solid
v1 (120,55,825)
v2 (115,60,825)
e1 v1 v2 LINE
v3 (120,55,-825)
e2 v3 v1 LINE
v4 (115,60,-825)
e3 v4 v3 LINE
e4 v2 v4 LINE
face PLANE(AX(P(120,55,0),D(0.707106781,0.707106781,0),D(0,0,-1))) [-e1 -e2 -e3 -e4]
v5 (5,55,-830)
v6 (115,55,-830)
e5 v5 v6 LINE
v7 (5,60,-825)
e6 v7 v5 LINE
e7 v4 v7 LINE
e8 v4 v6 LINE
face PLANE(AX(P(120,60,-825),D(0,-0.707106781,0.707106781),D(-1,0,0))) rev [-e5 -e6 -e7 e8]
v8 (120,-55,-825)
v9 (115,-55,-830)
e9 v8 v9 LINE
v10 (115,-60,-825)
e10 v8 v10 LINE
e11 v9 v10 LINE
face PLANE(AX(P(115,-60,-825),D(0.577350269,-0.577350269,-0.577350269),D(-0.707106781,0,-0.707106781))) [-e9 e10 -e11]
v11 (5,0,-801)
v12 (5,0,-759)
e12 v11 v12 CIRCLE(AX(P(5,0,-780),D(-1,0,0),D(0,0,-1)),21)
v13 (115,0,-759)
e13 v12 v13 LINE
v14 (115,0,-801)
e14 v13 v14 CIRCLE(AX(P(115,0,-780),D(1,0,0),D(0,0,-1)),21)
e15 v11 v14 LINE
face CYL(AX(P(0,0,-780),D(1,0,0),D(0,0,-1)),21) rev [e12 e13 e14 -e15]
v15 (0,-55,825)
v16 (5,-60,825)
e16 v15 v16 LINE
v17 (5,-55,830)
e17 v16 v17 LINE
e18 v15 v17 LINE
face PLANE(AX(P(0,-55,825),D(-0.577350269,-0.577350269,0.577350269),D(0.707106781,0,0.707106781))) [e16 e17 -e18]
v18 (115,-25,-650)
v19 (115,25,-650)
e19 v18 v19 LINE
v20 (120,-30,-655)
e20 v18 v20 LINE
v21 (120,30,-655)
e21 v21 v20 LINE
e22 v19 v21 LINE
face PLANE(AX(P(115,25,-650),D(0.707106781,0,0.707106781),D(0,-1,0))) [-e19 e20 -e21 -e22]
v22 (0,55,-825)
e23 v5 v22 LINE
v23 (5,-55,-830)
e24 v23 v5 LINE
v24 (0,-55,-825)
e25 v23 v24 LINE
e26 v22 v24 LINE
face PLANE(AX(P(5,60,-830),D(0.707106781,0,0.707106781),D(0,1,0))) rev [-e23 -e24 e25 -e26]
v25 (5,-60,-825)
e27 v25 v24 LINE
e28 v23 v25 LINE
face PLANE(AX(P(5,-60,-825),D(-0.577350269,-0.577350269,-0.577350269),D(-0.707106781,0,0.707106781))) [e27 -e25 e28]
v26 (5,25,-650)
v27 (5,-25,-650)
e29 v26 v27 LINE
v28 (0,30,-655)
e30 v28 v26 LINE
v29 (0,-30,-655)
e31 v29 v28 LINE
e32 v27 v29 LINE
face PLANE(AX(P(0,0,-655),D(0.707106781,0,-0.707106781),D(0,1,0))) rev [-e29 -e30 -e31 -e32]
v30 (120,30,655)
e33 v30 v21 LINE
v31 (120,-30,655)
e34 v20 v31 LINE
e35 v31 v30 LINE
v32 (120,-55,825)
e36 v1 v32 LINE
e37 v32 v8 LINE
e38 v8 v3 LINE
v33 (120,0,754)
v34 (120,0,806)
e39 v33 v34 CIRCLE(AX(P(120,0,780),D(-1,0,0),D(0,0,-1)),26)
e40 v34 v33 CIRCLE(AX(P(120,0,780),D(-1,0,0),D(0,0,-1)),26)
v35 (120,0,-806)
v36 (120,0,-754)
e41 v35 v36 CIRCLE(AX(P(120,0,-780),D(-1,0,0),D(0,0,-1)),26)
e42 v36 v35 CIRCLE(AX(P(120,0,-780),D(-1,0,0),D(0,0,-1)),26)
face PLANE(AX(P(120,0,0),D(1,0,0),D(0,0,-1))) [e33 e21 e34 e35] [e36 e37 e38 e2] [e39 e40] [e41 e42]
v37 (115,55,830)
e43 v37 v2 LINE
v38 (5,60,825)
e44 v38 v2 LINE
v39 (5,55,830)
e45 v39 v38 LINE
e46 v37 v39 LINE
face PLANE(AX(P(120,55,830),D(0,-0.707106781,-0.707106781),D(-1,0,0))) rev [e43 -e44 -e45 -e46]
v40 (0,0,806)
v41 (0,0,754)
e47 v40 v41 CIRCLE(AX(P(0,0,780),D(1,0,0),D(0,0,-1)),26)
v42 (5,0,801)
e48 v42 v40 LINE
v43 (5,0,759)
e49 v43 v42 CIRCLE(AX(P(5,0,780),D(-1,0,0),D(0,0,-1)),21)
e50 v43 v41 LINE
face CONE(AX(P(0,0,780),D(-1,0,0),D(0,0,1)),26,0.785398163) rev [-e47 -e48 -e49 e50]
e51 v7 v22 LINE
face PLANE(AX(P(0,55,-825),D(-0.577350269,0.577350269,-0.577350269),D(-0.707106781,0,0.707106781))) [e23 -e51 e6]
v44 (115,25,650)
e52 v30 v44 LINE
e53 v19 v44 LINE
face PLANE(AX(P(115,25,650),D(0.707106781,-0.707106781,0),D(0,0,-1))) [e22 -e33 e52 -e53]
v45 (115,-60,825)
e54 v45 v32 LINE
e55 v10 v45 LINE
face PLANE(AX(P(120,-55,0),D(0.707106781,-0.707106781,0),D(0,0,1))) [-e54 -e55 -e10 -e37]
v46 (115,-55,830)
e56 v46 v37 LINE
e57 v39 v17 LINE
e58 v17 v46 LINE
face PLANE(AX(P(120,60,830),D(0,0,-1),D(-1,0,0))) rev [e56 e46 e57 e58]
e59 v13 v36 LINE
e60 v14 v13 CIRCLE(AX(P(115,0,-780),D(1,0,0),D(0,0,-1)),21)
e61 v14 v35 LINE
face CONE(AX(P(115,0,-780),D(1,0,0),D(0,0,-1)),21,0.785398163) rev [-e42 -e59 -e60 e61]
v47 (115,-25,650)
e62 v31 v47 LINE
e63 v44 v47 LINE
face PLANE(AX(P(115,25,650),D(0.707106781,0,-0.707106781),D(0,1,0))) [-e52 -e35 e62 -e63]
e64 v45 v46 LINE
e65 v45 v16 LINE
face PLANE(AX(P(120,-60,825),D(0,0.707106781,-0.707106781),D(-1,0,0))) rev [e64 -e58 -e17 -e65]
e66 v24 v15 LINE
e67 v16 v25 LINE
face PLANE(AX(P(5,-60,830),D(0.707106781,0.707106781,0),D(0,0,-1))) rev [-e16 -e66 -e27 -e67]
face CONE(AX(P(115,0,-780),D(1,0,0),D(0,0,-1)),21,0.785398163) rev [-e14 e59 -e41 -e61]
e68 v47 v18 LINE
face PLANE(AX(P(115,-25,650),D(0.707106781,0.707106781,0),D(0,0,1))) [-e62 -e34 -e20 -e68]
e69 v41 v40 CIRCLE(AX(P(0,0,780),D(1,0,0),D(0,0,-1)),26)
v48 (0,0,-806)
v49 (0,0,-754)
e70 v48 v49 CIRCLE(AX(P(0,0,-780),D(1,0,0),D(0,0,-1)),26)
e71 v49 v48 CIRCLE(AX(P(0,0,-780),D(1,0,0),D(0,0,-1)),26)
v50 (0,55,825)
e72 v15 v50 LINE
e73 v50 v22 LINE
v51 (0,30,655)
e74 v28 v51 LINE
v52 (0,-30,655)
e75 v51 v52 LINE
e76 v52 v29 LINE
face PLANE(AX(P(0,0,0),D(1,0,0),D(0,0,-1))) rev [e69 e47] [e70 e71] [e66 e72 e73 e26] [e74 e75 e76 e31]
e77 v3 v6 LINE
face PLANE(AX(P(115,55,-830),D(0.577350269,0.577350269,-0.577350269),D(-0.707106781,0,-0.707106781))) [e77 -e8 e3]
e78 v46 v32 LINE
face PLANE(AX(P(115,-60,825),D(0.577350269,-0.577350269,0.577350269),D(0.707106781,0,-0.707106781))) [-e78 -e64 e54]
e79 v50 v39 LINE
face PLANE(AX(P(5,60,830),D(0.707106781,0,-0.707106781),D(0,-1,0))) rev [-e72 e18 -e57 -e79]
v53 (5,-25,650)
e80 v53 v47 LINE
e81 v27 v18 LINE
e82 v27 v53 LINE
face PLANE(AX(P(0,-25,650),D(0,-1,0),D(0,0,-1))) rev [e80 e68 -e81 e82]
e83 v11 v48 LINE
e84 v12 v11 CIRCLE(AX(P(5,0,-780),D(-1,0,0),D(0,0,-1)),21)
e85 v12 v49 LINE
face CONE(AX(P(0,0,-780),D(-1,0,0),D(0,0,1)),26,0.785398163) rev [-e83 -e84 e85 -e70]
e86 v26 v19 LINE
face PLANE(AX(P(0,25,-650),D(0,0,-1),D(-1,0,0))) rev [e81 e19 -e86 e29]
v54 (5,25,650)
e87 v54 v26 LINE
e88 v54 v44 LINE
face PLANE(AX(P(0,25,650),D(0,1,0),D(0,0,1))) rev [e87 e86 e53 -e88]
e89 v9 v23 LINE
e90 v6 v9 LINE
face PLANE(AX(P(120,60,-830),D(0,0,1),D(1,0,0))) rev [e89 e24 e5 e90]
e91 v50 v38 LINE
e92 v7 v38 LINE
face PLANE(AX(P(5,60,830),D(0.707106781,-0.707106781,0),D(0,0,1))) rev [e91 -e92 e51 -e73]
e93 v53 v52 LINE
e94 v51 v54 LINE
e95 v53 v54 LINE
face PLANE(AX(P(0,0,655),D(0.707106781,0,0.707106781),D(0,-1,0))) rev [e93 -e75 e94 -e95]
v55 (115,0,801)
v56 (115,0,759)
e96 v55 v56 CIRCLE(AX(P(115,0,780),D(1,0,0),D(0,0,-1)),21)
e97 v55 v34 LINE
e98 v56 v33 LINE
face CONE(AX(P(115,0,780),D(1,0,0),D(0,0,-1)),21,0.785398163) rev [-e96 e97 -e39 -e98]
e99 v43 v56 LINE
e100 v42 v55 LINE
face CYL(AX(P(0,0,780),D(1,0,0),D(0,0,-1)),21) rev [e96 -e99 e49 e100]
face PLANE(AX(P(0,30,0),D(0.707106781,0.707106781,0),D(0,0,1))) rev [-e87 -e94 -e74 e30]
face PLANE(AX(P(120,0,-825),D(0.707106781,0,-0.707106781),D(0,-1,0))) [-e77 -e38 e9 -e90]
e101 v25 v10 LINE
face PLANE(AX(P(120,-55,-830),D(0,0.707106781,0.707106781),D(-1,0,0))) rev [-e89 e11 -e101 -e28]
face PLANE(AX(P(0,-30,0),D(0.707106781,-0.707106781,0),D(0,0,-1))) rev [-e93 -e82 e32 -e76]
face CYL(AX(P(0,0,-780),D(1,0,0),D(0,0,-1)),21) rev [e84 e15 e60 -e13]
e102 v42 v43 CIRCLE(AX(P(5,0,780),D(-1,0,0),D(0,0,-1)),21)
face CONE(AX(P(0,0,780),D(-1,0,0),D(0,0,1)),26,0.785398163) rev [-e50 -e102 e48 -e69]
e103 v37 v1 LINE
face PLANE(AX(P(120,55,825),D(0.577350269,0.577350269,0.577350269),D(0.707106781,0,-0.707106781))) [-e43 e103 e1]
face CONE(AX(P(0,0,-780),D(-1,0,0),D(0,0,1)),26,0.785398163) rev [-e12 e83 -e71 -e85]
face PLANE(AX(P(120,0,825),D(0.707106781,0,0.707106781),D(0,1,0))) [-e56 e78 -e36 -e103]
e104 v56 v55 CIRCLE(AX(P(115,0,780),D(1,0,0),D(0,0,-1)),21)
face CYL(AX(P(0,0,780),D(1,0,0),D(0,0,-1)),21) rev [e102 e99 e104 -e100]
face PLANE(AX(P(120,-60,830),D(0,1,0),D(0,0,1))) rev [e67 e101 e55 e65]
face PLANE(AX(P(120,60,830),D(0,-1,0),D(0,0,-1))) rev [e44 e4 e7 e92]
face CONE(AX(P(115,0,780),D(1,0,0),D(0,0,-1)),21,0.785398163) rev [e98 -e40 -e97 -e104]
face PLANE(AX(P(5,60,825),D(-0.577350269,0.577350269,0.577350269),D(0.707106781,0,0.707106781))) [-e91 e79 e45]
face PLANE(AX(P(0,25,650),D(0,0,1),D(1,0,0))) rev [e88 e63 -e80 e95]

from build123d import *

# Parameters (mm, degrees)
SKETCH_1_W          = 1660
SKETCH_1_H          = 120
EXTRUDE_1_DEPTH     = 120
SKETCH_2_W          = 1300
SKETCH_2_H          = 50
CUT_EXTRUDE_1_DEPTH = 841.773453434
SKETCH_3_R          = 21
CUT_EXTRUDE_2_DEPTH = 841.773453434
CHAMFER_1_SIZE      = 5


with BuildPart() as part:
    # 草图1 → 凸台-拉伸1 (new body)
    with BuildSketch(Plane(origin=(0, 0, 0), x_dir=(0, 0, -1), z_dir=(1, 0, 0))):
        Rectangle(SKETCH_1_W, SKETCH_1_H)
    extrude(amount=EXTRUDE_1_DEPTH)

    # 草图2 → 切除-拉伸1 (cut, through all)
    with BuildSketch(Plane(origin=(120, 0, 0), x_dir=(0, 0, -1), z_dir=(1, 0, 0))):
        Rectangle(SKETCH_2_W, SKETCH_2_H)
    extrude(amount=-CUT_EXTRUDE_1_DEPTH, mode=Mode.SUBTRACT)

    # 草图3 → 切除-拉伸2 (cut, through all)
    with BuildSketch(Plane(origin=(120, 0, 0), x_dir=(0, 0, -1), z_dir=(1, 0, 0))):
        with Locations((-780, 0)):
            Circle(SKETCH_3_R)
        with Locations((780, 0)):
            Circle(SKETCH_3_R)
    extrude(amount=-CUT_EXTRUDE_2_DEPTH, mode=Mode.SUBTRACT)

    # 倒角1
    chamfer_1_edges = [part.edges().sort_by_distance(p)[0] for p in [
        (120, 0, 830),
        (120, -60, 0),
        (0, 0, -650),
        (0, -25, 0),
        (0, 0, 650),
        (0, 25, 0),
        (120, 0, -650),
        (120, 25, 0),
        (120, 0, 650),
        (120, -25, 0),
        (0, 0, 801),
        (120, 0, 801),
        (0, 0, -759),
        (120, 0, -759),
        (120, 0, -830),
        (0, -60, 0),
        (0, 0, 830),
        (0, 60, 0),
        (0, 0, -830),
        (120, 60, 0),
        (60, -60, -830),
        (60, -60, 830),
        (60, 60, 830),
        (60, 60, -830),
    ]]
    chamfer(chamfer_1_edges, length=CHAMFER_1_SIZE)


solid = part.part
